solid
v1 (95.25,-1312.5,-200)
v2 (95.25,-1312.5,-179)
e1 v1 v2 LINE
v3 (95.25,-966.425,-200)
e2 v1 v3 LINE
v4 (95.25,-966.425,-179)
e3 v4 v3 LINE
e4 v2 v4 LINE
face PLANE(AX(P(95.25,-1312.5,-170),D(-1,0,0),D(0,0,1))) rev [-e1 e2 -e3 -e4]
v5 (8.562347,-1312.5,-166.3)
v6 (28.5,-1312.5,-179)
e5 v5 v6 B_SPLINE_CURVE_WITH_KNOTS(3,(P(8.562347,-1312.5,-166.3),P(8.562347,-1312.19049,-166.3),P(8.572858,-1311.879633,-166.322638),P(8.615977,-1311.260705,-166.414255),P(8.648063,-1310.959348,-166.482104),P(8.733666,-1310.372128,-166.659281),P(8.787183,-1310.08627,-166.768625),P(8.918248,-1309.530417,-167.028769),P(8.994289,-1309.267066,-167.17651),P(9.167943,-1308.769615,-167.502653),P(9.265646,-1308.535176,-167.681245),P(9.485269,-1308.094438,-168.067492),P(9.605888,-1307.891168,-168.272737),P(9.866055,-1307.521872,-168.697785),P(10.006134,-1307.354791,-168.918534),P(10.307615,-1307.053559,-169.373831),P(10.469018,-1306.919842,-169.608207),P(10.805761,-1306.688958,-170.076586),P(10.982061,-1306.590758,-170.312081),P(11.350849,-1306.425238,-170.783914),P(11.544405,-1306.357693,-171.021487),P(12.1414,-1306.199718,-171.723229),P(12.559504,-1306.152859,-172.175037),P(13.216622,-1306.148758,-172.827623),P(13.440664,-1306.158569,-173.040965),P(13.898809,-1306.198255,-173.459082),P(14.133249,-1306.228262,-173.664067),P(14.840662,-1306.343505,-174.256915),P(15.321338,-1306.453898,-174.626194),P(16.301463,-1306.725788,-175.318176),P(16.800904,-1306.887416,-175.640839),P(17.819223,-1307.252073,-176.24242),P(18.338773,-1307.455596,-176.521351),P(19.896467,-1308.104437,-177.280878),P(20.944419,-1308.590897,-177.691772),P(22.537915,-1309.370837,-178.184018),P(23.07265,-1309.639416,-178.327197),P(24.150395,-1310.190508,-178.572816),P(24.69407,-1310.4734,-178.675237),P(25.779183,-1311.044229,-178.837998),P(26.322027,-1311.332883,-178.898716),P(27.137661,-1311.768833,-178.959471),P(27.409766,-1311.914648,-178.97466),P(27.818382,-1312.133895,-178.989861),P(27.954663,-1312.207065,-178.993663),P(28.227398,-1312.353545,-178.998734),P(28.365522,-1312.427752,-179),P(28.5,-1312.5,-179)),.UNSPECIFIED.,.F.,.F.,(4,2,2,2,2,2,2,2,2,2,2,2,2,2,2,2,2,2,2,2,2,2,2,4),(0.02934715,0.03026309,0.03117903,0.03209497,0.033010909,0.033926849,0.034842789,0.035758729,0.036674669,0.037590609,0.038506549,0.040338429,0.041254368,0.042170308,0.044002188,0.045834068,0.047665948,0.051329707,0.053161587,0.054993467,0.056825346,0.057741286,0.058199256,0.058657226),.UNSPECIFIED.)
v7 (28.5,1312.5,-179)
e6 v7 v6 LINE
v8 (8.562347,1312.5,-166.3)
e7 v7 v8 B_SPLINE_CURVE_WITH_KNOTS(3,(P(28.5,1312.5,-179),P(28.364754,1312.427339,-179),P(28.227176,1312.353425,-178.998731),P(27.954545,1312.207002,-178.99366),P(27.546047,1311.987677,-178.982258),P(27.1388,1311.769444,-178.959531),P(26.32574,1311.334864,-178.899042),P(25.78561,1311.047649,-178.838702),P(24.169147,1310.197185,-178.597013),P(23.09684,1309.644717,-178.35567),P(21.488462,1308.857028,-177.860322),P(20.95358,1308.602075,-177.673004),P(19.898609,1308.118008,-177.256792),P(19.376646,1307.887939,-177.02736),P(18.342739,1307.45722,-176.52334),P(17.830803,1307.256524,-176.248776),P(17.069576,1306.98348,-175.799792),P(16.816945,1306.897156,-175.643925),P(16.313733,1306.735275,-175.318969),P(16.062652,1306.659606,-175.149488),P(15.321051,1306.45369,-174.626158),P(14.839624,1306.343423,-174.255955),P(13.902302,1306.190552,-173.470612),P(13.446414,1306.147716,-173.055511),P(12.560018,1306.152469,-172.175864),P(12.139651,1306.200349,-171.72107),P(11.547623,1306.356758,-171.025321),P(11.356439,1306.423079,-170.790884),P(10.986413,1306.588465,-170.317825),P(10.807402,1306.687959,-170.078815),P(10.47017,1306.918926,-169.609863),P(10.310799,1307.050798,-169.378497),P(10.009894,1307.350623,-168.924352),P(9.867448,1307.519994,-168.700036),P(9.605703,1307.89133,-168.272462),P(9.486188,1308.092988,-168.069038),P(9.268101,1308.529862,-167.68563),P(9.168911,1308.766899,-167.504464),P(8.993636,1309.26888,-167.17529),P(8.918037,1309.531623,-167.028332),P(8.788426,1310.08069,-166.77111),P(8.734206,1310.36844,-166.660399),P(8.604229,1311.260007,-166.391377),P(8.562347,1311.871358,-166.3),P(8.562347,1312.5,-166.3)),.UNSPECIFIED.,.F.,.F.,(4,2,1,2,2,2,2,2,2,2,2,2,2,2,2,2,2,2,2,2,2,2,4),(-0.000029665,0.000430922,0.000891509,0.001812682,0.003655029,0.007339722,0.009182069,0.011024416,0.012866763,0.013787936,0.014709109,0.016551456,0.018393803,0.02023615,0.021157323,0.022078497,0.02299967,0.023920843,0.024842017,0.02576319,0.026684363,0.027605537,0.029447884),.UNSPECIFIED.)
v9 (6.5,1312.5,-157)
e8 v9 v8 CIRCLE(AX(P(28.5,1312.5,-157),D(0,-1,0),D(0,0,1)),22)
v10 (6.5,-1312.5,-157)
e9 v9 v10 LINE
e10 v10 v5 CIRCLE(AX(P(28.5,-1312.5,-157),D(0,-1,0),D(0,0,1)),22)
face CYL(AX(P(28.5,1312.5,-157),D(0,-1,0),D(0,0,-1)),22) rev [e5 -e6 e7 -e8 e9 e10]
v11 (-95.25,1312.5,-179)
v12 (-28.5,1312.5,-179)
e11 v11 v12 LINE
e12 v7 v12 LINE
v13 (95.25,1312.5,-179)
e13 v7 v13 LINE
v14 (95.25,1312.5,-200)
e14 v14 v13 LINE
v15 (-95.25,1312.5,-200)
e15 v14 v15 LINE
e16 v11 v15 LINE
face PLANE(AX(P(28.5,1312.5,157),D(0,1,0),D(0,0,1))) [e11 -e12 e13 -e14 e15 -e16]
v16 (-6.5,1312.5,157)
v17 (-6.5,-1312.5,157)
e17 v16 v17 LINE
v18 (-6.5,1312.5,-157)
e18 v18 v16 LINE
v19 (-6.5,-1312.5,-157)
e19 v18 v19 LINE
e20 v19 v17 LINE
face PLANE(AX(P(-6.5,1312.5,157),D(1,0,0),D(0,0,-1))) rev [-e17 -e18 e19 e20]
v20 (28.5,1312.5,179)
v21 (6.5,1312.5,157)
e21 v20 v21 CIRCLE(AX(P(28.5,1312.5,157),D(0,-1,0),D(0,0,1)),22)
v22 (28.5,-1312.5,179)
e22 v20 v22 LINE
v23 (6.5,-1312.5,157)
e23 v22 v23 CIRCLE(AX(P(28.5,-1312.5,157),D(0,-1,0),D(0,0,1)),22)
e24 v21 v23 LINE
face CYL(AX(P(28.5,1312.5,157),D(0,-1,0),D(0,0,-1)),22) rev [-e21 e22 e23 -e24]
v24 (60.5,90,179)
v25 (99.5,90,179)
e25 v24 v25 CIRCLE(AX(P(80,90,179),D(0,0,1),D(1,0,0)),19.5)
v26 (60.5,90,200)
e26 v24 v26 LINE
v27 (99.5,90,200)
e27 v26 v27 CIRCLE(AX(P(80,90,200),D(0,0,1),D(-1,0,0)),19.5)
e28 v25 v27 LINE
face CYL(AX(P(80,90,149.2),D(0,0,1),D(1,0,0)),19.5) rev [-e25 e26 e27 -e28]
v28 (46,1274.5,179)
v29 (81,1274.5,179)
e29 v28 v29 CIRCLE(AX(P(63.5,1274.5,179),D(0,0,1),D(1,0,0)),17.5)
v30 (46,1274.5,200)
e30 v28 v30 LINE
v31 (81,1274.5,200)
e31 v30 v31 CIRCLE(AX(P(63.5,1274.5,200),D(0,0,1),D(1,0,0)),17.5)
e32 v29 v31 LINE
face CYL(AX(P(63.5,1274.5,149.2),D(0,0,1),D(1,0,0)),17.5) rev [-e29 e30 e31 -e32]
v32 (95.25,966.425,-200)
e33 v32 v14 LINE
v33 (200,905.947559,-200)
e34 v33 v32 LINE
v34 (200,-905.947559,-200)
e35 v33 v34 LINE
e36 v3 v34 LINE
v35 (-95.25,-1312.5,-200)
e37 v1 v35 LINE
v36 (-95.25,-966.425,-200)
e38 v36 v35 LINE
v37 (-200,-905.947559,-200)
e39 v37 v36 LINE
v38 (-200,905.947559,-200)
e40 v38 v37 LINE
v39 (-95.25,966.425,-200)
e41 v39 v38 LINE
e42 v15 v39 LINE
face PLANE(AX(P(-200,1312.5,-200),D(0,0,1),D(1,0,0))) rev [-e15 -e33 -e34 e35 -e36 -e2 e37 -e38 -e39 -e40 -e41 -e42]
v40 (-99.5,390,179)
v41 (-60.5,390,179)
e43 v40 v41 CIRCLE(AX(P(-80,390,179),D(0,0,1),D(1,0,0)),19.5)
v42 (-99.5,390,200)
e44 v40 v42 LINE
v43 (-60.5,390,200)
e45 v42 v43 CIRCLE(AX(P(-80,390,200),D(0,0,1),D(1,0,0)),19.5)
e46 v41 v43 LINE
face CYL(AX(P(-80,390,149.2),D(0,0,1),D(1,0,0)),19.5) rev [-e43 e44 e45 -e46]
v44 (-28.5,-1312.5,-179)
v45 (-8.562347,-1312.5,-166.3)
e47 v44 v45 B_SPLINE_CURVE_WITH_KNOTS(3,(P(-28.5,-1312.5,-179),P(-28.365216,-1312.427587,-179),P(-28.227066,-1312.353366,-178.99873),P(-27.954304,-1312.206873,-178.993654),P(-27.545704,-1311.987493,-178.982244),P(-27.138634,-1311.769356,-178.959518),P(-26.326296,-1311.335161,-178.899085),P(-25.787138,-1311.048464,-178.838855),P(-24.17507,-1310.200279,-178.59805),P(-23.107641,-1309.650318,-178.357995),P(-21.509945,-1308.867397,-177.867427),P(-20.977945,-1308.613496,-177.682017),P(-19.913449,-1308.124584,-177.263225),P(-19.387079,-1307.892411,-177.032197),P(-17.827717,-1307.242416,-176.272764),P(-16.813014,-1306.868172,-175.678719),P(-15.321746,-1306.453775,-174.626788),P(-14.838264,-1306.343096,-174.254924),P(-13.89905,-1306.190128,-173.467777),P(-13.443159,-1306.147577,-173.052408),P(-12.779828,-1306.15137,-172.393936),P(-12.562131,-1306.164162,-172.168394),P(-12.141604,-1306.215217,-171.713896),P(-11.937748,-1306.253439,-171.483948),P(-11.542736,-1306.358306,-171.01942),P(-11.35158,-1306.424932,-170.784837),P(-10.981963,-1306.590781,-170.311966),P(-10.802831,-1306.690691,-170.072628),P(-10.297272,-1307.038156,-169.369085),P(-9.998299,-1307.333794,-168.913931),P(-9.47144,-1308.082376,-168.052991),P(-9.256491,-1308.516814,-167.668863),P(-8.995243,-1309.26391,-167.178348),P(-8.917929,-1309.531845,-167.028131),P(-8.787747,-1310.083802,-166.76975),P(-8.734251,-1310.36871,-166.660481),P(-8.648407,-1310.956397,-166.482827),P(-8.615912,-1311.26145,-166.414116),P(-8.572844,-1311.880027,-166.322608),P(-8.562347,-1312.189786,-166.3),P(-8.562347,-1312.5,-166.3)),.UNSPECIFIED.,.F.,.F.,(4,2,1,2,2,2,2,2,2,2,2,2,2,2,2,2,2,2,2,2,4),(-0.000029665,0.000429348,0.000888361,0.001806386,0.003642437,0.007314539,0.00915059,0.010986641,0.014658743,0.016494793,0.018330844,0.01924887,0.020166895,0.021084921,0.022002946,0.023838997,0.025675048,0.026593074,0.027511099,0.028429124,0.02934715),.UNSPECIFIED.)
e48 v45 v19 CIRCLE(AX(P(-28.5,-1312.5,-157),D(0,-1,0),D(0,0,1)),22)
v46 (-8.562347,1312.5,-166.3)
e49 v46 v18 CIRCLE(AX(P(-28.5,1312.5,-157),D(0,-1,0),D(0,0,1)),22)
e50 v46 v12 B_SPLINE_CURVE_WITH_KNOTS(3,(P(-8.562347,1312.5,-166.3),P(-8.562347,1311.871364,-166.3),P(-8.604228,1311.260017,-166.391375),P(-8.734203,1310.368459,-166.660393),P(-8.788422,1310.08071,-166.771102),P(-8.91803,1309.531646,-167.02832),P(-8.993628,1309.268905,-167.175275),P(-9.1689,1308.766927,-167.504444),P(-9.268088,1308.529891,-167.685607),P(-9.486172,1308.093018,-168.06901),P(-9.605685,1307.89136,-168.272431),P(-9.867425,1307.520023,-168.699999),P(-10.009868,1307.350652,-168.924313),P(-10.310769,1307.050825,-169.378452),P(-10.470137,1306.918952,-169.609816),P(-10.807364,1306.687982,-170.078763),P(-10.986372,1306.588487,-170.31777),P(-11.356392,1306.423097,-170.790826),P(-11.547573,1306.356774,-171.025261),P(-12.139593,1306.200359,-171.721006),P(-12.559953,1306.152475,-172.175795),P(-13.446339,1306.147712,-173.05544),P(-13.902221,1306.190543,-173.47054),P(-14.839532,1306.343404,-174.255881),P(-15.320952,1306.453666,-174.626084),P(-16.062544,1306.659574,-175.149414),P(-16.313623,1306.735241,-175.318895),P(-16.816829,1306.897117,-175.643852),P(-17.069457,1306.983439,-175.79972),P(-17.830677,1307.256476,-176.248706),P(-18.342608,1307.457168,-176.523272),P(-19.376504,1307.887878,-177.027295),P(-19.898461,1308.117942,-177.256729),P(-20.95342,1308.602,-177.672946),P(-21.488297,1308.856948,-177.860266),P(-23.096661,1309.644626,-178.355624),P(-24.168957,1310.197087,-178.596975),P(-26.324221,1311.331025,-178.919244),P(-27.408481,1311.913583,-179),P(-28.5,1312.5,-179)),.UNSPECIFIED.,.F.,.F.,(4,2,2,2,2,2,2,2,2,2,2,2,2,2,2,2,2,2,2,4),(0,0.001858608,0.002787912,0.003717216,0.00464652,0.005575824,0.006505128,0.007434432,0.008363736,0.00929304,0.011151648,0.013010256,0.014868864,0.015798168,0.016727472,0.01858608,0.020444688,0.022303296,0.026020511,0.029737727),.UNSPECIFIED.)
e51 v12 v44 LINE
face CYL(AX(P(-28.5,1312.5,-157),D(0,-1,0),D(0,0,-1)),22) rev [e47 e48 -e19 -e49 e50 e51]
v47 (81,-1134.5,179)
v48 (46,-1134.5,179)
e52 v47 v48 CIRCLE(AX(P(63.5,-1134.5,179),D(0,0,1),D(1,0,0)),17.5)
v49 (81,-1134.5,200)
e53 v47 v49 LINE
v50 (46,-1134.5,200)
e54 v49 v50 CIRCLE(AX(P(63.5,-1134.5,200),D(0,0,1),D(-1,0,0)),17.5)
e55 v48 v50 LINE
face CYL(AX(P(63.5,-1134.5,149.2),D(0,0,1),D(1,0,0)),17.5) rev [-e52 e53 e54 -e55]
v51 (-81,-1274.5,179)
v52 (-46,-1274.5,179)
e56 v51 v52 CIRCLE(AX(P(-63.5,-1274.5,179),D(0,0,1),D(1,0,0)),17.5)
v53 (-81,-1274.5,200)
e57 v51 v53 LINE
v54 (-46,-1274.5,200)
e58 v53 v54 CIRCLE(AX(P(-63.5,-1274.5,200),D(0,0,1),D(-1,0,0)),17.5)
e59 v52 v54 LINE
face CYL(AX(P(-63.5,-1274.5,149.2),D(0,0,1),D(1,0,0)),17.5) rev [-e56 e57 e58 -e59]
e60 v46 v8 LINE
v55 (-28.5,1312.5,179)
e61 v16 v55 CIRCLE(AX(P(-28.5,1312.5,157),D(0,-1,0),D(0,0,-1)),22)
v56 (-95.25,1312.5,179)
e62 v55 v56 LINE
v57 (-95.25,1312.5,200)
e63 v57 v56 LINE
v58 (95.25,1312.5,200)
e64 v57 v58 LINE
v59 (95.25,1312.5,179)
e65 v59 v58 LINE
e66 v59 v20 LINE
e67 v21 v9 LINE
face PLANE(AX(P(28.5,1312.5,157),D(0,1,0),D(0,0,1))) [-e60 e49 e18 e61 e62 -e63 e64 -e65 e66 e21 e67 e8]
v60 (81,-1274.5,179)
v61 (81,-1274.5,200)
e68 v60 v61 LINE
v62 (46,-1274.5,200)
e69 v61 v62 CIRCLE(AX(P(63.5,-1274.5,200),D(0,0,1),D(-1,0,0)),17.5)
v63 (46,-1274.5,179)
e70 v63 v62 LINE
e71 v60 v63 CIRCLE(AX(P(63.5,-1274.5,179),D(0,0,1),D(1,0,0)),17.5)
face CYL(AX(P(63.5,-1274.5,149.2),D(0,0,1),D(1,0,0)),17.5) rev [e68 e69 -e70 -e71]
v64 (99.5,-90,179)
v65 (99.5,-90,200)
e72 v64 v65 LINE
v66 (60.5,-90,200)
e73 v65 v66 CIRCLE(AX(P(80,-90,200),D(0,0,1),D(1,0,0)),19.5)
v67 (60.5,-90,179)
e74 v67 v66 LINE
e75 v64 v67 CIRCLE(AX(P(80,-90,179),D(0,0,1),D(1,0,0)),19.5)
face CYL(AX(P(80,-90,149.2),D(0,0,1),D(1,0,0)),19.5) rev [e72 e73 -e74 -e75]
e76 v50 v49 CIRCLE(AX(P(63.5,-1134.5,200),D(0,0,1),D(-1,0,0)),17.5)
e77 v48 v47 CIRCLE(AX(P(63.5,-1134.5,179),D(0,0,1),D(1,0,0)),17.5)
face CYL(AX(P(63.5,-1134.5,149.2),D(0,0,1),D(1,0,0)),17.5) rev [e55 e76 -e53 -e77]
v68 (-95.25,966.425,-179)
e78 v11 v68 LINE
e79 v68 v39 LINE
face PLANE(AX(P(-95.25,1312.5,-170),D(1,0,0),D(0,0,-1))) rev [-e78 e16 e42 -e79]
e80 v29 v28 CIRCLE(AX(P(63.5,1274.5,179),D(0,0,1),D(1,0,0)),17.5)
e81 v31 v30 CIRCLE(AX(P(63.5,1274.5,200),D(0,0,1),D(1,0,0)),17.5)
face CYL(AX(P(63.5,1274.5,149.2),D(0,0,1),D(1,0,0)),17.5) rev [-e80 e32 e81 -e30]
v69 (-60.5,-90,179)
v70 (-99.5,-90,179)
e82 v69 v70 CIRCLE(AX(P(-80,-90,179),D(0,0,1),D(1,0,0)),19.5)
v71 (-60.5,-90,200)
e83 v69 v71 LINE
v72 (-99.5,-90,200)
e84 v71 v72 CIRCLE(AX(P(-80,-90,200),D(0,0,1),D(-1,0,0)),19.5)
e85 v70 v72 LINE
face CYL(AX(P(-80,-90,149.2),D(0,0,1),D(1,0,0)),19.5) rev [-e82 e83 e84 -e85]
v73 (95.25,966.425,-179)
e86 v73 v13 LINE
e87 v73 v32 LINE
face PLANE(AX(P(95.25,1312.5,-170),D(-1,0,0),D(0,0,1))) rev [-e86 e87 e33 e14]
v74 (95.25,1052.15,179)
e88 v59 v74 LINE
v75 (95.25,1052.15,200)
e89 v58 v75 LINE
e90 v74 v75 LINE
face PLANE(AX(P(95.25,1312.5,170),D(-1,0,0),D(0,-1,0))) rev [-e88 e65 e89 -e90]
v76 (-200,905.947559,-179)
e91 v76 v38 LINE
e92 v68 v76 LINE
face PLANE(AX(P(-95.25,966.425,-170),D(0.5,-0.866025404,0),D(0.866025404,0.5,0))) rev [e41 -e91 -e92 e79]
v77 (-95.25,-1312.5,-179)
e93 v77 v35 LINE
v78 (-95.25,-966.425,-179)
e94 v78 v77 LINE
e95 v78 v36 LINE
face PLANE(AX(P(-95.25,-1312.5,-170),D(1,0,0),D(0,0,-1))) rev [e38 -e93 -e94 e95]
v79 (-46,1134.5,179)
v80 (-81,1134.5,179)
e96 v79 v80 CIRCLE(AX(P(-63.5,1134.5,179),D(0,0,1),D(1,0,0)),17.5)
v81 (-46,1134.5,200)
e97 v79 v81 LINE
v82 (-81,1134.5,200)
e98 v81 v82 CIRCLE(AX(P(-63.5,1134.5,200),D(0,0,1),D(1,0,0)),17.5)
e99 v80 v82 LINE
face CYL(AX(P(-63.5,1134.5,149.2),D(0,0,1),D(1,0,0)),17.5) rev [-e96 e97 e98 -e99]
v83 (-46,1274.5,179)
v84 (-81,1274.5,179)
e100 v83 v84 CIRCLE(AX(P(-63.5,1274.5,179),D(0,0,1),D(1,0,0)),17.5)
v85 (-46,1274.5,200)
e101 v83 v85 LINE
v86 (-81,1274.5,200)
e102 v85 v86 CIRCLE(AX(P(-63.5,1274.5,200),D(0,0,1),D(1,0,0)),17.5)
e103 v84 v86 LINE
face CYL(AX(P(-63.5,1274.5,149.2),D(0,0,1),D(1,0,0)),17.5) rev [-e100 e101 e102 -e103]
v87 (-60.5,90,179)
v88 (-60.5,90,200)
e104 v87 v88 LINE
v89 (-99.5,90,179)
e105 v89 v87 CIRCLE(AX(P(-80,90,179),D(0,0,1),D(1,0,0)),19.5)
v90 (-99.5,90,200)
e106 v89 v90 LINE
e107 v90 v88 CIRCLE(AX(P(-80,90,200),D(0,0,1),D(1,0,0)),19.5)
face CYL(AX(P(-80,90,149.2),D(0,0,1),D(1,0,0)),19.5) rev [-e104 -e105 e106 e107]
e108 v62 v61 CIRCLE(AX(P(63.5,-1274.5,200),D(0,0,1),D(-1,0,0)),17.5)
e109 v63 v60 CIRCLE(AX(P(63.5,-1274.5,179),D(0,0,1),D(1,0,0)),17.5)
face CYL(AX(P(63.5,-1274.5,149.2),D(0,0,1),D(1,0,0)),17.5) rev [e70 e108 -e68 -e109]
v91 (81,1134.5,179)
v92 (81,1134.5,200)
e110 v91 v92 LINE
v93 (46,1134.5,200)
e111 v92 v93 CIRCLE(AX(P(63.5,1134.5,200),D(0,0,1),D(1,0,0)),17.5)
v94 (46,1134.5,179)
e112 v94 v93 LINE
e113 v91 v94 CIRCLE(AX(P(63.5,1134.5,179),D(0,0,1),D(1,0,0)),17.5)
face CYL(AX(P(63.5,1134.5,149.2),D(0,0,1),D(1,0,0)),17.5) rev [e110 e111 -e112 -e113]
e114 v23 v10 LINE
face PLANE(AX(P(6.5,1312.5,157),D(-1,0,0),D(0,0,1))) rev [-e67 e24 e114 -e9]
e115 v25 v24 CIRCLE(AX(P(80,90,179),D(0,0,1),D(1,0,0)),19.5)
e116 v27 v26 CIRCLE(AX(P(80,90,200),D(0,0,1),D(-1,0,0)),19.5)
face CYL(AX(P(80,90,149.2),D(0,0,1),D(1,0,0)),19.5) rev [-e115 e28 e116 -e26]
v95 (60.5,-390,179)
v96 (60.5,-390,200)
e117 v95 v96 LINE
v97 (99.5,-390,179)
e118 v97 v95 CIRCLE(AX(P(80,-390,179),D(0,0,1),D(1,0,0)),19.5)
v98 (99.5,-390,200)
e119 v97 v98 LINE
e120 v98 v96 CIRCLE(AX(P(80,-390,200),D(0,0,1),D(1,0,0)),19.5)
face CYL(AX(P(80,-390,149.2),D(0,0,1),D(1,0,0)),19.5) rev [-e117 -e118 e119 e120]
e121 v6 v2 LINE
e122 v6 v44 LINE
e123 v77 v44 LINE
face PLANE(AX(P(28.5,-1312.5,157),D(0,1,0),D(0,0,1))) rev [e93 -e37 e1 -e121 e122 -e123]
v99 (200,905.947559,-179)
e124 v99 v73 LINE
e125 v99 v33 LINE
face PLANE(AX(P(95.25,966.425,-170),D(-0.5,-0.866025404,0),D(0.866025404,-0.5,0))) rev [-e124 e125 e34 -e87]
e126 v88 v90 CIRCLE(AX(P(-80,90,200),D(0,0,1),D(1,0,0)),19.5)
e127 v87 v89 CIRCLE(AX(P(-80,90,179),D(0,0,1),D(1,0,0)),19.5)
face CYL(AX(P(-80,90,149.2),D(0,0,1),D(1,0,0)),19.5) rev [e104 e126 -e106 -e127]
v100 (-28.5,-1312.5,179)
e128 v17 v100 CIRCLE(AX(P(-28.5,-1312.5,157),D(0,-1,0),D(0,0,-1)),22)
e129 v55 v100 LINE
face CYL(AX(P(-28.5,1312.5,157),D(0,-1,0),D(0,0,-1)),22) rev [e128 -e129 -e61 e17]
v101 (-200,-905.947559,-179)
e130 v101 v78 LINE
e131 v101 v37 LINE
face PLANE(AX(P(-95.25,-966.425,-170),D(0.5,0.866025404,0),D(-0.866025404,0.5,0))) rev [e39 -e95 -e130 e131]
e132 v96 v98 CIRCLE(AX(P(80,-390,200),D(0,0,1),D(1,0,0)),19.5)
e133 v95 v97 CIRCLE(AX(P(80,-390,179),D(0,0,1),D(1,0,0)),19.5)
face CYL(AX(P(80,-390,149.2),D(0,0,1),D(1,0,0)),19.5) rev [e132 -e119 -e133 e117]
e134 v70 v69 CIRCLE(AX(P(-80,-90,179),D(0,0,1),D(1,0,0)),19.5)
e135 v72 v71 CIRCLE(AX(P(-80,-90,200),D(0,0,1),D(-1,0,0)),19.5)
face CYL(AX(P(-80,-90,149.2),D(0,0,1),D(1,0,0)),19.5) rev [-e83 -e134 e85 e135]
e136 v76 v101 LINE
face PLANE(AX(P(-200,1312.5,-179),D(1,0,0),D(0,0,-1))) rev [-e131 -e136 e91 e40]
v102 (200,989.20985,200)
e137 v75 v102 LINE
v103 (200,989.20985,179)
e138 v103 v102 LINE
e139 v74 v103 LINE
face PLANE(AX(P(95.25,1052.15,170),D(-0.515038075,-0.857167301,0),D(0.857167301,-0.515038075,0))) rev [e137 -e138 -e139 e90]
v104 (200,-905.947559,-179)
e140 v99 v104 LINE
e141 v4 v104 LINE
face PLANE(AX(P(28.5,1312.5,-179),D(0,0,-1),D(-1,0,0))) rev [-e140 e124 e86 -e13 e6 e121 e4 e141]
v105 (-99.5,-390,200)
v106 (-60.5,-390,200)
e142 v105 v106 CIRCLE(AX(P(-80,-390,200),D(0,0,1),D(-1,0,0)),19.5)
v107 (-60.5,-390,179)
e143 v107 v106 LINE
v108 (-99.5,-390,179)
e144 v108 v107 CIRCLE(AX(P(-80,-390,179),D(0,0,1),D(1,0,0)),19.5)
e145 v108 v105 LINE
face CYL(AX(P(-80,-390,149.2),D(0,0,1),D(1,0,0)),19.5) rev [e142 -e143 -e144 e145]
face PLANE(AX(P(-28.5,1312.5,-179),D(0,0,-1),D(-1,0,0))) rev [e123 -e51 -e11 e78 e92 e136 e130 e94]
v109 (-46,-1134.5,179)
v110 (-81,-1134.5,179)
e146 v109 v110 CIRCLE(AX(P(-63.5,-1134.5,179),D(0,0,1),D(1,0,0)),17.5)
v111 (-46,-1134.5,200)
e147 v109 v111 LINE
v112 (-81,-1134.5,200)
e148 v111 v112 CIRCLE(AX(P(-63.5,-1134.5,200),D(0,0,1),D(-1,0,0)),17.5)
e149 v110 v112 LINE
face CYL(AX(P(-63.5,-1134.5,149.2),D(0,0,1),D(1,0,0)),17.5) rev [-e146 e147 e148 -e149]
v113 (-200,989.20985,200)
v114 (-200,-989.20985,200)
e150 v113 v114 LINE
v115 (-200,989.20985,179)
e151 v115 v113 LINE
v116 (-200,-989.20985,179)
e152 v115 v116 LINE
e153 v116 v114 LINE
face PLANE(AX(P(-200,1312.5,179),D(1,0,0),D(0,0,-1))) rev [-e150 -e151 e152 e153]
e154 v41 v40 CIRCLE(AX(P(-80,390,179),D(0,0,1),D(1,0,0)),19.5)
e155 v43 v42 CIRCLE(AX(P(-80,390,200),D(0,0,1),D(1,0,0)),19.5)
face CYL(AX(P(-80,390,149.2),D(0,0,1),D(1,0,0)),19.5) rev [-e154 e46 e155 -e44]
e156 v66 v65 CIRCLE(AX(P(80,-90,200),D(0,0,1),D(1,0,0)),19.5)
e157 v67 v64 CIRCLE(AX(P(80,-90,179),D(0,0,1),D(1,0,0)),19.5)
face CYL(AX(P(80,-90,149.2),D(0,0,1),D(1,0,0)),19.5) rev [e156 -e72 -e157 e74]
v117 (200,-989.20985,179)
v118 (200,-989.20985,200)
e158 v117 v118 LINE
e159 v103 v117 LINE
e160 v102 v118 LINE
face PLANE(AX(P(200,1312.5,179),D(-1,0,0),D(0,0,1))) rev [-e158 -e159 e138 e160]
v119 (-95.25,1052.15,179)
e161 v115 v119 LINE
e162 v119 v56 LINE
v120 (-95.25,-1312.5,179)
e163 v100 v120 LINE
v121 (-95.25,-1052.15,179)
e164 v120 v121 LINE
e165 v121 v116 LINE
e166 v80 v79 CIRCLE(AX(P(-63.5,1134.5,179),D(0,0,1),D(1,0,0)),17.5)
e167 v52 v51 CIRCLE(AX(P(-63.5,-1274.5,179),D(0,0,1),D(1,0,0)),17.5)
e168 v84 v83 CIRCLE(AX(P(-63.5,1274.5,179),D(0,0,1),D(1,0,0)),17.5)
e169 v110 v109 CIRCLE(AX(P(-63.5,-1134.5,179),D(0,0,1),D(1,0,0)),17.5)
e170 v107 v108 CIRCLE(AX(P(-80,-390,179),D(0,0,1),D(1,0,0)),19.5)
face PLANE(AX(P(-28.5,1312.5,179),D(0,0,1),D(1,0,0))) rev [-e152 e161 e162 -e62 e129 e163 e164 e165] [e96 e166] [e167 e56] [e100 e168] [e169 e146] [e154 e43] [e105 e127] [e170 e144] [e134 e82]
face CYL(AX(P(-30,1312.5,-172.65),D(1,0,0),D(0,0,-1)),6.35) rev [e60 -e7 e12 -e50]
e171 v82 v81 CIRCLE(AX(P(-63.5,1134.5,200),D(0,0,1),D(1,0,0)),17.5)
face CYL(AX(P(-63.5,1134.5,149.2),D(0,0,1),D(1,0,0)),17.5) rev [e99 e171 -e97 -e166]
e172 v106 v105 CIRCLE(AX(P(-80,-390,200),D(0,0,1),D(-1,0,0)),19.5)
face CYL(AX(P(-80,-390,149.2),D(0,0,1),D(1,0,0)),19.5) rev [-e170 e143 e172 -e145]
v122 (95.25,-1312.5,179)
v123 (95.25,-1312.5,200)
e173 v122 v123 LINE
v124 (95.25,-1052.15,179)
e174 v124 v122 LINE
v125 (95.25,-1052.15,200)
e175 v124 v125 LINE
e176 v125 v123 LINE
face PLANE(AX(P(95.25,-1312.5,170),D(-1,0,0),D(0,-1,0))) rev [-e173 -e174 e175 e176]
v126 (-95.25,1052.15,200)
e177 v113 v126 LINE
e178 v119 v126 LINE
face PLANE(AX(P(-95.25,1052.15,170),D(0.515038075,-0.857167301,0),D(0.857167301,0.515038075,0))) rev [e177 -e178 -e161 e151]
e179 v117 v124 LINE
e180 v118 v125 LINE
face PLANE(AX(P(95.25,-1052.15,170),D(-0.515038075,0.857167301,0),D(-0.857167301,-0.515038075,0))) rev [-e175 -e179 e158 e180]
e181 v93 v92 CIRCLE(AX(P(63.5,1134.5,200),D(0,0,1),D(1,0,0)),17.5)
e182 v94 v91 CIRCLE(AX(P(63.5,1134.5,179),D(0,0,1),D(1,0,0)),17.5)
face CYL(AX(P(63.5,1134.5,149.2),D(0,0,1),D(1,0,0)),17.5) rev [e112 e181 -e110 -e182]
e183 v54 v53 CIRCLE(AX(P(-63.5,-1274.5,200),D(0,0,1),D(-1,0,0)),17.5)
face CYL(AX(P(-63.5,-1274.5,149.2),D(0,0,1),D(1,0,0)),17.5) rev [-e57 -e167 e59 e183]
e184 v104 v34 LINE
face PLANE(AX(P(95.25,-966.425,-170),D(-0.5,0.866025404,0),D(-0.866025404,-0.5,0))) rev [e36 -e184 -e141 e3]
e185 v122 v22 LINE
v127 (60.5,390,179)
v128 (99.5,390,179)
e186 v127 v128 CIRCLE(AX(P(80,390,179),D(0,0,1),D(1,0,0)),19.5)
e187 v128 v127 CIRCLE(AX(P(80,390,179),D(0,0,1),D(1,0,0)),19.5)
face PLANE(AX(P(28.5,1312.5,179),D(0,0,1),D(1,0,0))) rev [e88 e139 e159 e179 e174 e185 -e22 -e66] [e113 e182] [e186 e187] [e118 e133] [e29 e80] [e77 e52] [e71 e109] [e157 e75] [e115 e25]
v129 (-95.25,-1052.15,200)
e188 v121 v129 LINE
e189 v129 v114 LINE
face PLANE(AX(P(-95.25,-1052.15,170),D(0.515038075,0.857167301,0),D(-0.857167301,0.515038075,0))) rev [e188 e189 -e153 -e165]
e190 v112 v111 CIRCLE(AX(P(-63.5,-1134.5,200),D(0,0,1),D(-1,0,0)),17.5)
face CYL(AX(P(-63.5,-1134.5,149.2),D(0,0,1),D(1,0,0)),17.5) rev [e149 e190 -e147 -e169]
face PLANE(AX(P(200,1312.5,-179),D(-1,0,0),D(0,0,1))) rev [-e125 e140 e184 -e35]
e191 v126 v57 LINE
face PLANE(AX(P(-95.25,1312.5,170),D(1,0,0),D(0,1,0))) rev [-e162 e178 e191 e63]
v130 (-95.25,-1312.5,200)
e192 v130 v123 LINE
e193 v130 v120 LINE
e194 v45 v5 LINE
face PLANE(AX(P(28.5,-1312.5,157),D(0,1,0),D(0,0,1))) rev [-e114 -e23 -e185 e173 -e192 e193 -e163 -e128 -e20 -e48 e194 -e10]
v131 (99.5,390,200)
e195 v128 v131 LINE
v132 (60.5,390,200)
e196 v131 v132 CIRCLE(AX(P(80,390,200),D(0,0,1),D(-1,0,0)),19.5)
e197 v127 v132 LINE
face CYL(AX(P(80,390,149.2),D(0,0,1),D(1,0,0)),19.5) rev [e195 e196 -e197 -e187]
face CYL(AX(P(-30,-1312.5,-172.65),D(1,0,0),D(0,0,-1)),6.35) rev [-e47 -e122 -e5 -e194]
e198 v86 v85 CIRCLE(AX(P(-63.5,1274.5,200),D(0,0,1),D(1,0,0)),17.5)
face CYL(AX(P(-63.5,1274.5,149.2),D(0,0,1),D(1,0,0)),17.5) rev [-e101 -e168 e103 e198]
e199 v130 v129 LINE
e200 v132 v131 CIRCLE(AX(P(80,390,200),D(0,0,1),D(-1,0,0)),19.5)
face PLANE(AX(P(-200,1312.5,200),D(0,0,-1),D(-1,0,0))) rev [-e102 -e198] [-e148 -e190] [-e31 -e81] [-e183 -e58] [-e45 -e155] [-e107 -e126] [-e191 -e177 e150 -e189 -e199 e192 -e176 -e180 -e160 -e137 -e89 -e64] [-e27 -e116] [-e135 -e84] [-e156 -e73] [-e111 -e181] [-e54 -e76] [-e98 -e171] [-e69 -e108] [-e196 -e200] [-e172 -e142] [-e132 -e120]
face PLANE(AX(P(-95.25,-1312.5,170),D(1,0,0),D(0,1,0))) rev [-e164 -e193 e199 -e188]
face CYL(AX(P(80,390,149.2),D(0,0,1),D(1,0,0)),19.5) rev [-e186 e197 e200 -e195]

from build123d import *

# Parameters (mm, degrees)
EXTRUDE1_DEPTH     = 1312.5
CUT_EXTRUDE2_DEPTH = 30
CUT_EXTRUDE3_DEPTH = 30
SKETCH2_R          = 19.5
SKETCH2_R_2        = 17.5
CUT_EXTRUDE1_DEPTH = 50.8
SKETCH6_R          = 6.35
CUT_EXTRUDE4_DEPTH = 30


with BuildPart() as part:
    # Sketch1 → Extrude1 (new, symmetric)
    with BuildSketch(Plane(origin=(0, 0, 0), x_dir=(1, 0, 0), z_dir=(0, 1, 0))):
        with BuildLine():
            Line((-6.5, -157), (-6.5, 157))
            ThreePointArc((-6.5, 157), (-12.943650814, 172.556349186), (-28.5, 179))
            Line((-28.5, 179), (-200, 179))
            Line((-200, 179), (-200, 200))
            Line((-200, 200), (200, 200))
            Line((200, 200), (200, 179))
            Line((200, 179), (28.5, 179))
            ThreePointArc((28.5, 179), (12.943650814, 172.556349186), (6.5, 157))
            Line((6.5, 157), (6.5, -157))
            ThreePointArc((6.5, -157), (12.943650814, -172.556349186), (28.5, -179))
            Line((28.5, -179), (200, -179))
            Line((200, -179), (200, -200))
            Line((200, -200), (-200, -200))
            Line((-200, -200), (-200, -179))
            Line((-200, -179), (-28.5, -179))
            ThreePointArc((-28.5, -179), (-12.943650814, -172.556349186), (-6.5, -157))
        make_face()
    extrude(amount=EXTRUDE1_DEPTH, both=True)

    # Sketch3 → Cut-Extrude2 (cut)
    with BuildSketch(Plane.XY.offset(200)):
        Polygon((-95.25, 1312.5), (-95.25, 1052.15), (-200, 989.209850157), (-200, 1312.5), align=None)
        Polygon((95.25, 1052.15), (200, 989.209850157), (200, 1312.5), (95.25, 1312.5), align=None)
        Polygon((200, -989.209850157), (200, -1312.5), (95.25, -1312.5), (95.25, -1052.15), align=None)
        Polygon((-200, -1312.5), (-95.25, -1312.5), (-95.25, -1052.15), (-200, -989.209850157), align=None)
    extrude(amount=-CUT_EXTRUDE2_DEPTH, mode=Mode.SUBTRACT)

    # Sketch5 → Cut-Extrude3 (cut)
    with BuildSketch(Plane(origin=(0, 0, -200), x_dir=(-1, 0, 0), z_dir=(0, 0, -1))):
        Polygon((-200, 1312.5), (-95.25, 1312.5), (-95.25, 966.425), (-200, 905.947559302), align=None)
        Polygon((200, 905.947559302), (200, 1312.5), (95.25, 1312.5), (95.25, 966.425), align=None)
        Polygon((200, -1312.5), (95.25, -1312.5), (95.25, -966.425), (200, -905.947559302), align=None)
        Polygon((-200, -905.947559302), (-200, -1312.5), (-95.25, -1312.5), (-95.25, -966.425), align=None)
    extrude(amount=-CUT_EXTRUDE3_DEPTH, mode=Mode.SUBTRACT)

    # Sketch2 → Cut-Extrude1 (cut)
    with BuildSketch(Plane.XY.offset(200)):
        with Locations((-80, 390)):
            Circle(SKETCH2_R)
        with Locations((80, 390)):
            Circle(SKETCH2_R)
        with Locations((80, -390)):
            Circle(SKETCH2_R)
        with Locations((-80, -390)):
            Circle(SKETCH2_R)
        with Locations((63.5, 1274.5)):
            Circle(SKETCH2_R_2)
        with Locations((63.5, 1134.5)):
            Circle(SKETCH2_R_2)
        with Locations((-63.5, 1274.5)):
            Circle(SKETCH2_R_2)
        with Locations((-63.5, 1134.5)):
            Circle(SKETCH2_R_2)
        with Locations((63.5, -1134.5)):
            Circle(SKETCH2_R_2)
        with Locations((-63.5, -1134.5)):
            Circle(SKETCH2_R_2)
        with Locations((63.5, -1274.5)):
            Circle(SKETCH2_R_2)
        with Locations((-63.5, -1274.5)):
            Circle(SKETCH2_R_2)
        with Locations((-80, 90)):
            Circle(SKETCH2_R)
        with Locations((80, 90)):
            Circle(SKETCH2_R)
        with Locations((-80, -90)):
            Circle(SKETCH2_R)
        with Locations((80, -90)):
            Circle(SKETCH2_R)
    extrude(amount=-CUT_EXTRUDE1_DEPTH, mode=Mode.SUBTRACT)

    # Sketch6 → Cut-Extrude4 (cut, symmetric)
    with BuildSketch(Plane(origin=(0, 0, 0), x_dir=(0, 0, -1), z_dir=(1, 0, 0))):
        with Locations((172.65, 1312.5)):
            Circle(SKETCH6_R)
        with Locations((172.65, -1312.5)):
            Circle(SKETCH6_R)
    extrude(amount=CUT_EXTRUDE4_DEPTH, both=True, mode=Mode.SUBTRACT)


solid = part.part
